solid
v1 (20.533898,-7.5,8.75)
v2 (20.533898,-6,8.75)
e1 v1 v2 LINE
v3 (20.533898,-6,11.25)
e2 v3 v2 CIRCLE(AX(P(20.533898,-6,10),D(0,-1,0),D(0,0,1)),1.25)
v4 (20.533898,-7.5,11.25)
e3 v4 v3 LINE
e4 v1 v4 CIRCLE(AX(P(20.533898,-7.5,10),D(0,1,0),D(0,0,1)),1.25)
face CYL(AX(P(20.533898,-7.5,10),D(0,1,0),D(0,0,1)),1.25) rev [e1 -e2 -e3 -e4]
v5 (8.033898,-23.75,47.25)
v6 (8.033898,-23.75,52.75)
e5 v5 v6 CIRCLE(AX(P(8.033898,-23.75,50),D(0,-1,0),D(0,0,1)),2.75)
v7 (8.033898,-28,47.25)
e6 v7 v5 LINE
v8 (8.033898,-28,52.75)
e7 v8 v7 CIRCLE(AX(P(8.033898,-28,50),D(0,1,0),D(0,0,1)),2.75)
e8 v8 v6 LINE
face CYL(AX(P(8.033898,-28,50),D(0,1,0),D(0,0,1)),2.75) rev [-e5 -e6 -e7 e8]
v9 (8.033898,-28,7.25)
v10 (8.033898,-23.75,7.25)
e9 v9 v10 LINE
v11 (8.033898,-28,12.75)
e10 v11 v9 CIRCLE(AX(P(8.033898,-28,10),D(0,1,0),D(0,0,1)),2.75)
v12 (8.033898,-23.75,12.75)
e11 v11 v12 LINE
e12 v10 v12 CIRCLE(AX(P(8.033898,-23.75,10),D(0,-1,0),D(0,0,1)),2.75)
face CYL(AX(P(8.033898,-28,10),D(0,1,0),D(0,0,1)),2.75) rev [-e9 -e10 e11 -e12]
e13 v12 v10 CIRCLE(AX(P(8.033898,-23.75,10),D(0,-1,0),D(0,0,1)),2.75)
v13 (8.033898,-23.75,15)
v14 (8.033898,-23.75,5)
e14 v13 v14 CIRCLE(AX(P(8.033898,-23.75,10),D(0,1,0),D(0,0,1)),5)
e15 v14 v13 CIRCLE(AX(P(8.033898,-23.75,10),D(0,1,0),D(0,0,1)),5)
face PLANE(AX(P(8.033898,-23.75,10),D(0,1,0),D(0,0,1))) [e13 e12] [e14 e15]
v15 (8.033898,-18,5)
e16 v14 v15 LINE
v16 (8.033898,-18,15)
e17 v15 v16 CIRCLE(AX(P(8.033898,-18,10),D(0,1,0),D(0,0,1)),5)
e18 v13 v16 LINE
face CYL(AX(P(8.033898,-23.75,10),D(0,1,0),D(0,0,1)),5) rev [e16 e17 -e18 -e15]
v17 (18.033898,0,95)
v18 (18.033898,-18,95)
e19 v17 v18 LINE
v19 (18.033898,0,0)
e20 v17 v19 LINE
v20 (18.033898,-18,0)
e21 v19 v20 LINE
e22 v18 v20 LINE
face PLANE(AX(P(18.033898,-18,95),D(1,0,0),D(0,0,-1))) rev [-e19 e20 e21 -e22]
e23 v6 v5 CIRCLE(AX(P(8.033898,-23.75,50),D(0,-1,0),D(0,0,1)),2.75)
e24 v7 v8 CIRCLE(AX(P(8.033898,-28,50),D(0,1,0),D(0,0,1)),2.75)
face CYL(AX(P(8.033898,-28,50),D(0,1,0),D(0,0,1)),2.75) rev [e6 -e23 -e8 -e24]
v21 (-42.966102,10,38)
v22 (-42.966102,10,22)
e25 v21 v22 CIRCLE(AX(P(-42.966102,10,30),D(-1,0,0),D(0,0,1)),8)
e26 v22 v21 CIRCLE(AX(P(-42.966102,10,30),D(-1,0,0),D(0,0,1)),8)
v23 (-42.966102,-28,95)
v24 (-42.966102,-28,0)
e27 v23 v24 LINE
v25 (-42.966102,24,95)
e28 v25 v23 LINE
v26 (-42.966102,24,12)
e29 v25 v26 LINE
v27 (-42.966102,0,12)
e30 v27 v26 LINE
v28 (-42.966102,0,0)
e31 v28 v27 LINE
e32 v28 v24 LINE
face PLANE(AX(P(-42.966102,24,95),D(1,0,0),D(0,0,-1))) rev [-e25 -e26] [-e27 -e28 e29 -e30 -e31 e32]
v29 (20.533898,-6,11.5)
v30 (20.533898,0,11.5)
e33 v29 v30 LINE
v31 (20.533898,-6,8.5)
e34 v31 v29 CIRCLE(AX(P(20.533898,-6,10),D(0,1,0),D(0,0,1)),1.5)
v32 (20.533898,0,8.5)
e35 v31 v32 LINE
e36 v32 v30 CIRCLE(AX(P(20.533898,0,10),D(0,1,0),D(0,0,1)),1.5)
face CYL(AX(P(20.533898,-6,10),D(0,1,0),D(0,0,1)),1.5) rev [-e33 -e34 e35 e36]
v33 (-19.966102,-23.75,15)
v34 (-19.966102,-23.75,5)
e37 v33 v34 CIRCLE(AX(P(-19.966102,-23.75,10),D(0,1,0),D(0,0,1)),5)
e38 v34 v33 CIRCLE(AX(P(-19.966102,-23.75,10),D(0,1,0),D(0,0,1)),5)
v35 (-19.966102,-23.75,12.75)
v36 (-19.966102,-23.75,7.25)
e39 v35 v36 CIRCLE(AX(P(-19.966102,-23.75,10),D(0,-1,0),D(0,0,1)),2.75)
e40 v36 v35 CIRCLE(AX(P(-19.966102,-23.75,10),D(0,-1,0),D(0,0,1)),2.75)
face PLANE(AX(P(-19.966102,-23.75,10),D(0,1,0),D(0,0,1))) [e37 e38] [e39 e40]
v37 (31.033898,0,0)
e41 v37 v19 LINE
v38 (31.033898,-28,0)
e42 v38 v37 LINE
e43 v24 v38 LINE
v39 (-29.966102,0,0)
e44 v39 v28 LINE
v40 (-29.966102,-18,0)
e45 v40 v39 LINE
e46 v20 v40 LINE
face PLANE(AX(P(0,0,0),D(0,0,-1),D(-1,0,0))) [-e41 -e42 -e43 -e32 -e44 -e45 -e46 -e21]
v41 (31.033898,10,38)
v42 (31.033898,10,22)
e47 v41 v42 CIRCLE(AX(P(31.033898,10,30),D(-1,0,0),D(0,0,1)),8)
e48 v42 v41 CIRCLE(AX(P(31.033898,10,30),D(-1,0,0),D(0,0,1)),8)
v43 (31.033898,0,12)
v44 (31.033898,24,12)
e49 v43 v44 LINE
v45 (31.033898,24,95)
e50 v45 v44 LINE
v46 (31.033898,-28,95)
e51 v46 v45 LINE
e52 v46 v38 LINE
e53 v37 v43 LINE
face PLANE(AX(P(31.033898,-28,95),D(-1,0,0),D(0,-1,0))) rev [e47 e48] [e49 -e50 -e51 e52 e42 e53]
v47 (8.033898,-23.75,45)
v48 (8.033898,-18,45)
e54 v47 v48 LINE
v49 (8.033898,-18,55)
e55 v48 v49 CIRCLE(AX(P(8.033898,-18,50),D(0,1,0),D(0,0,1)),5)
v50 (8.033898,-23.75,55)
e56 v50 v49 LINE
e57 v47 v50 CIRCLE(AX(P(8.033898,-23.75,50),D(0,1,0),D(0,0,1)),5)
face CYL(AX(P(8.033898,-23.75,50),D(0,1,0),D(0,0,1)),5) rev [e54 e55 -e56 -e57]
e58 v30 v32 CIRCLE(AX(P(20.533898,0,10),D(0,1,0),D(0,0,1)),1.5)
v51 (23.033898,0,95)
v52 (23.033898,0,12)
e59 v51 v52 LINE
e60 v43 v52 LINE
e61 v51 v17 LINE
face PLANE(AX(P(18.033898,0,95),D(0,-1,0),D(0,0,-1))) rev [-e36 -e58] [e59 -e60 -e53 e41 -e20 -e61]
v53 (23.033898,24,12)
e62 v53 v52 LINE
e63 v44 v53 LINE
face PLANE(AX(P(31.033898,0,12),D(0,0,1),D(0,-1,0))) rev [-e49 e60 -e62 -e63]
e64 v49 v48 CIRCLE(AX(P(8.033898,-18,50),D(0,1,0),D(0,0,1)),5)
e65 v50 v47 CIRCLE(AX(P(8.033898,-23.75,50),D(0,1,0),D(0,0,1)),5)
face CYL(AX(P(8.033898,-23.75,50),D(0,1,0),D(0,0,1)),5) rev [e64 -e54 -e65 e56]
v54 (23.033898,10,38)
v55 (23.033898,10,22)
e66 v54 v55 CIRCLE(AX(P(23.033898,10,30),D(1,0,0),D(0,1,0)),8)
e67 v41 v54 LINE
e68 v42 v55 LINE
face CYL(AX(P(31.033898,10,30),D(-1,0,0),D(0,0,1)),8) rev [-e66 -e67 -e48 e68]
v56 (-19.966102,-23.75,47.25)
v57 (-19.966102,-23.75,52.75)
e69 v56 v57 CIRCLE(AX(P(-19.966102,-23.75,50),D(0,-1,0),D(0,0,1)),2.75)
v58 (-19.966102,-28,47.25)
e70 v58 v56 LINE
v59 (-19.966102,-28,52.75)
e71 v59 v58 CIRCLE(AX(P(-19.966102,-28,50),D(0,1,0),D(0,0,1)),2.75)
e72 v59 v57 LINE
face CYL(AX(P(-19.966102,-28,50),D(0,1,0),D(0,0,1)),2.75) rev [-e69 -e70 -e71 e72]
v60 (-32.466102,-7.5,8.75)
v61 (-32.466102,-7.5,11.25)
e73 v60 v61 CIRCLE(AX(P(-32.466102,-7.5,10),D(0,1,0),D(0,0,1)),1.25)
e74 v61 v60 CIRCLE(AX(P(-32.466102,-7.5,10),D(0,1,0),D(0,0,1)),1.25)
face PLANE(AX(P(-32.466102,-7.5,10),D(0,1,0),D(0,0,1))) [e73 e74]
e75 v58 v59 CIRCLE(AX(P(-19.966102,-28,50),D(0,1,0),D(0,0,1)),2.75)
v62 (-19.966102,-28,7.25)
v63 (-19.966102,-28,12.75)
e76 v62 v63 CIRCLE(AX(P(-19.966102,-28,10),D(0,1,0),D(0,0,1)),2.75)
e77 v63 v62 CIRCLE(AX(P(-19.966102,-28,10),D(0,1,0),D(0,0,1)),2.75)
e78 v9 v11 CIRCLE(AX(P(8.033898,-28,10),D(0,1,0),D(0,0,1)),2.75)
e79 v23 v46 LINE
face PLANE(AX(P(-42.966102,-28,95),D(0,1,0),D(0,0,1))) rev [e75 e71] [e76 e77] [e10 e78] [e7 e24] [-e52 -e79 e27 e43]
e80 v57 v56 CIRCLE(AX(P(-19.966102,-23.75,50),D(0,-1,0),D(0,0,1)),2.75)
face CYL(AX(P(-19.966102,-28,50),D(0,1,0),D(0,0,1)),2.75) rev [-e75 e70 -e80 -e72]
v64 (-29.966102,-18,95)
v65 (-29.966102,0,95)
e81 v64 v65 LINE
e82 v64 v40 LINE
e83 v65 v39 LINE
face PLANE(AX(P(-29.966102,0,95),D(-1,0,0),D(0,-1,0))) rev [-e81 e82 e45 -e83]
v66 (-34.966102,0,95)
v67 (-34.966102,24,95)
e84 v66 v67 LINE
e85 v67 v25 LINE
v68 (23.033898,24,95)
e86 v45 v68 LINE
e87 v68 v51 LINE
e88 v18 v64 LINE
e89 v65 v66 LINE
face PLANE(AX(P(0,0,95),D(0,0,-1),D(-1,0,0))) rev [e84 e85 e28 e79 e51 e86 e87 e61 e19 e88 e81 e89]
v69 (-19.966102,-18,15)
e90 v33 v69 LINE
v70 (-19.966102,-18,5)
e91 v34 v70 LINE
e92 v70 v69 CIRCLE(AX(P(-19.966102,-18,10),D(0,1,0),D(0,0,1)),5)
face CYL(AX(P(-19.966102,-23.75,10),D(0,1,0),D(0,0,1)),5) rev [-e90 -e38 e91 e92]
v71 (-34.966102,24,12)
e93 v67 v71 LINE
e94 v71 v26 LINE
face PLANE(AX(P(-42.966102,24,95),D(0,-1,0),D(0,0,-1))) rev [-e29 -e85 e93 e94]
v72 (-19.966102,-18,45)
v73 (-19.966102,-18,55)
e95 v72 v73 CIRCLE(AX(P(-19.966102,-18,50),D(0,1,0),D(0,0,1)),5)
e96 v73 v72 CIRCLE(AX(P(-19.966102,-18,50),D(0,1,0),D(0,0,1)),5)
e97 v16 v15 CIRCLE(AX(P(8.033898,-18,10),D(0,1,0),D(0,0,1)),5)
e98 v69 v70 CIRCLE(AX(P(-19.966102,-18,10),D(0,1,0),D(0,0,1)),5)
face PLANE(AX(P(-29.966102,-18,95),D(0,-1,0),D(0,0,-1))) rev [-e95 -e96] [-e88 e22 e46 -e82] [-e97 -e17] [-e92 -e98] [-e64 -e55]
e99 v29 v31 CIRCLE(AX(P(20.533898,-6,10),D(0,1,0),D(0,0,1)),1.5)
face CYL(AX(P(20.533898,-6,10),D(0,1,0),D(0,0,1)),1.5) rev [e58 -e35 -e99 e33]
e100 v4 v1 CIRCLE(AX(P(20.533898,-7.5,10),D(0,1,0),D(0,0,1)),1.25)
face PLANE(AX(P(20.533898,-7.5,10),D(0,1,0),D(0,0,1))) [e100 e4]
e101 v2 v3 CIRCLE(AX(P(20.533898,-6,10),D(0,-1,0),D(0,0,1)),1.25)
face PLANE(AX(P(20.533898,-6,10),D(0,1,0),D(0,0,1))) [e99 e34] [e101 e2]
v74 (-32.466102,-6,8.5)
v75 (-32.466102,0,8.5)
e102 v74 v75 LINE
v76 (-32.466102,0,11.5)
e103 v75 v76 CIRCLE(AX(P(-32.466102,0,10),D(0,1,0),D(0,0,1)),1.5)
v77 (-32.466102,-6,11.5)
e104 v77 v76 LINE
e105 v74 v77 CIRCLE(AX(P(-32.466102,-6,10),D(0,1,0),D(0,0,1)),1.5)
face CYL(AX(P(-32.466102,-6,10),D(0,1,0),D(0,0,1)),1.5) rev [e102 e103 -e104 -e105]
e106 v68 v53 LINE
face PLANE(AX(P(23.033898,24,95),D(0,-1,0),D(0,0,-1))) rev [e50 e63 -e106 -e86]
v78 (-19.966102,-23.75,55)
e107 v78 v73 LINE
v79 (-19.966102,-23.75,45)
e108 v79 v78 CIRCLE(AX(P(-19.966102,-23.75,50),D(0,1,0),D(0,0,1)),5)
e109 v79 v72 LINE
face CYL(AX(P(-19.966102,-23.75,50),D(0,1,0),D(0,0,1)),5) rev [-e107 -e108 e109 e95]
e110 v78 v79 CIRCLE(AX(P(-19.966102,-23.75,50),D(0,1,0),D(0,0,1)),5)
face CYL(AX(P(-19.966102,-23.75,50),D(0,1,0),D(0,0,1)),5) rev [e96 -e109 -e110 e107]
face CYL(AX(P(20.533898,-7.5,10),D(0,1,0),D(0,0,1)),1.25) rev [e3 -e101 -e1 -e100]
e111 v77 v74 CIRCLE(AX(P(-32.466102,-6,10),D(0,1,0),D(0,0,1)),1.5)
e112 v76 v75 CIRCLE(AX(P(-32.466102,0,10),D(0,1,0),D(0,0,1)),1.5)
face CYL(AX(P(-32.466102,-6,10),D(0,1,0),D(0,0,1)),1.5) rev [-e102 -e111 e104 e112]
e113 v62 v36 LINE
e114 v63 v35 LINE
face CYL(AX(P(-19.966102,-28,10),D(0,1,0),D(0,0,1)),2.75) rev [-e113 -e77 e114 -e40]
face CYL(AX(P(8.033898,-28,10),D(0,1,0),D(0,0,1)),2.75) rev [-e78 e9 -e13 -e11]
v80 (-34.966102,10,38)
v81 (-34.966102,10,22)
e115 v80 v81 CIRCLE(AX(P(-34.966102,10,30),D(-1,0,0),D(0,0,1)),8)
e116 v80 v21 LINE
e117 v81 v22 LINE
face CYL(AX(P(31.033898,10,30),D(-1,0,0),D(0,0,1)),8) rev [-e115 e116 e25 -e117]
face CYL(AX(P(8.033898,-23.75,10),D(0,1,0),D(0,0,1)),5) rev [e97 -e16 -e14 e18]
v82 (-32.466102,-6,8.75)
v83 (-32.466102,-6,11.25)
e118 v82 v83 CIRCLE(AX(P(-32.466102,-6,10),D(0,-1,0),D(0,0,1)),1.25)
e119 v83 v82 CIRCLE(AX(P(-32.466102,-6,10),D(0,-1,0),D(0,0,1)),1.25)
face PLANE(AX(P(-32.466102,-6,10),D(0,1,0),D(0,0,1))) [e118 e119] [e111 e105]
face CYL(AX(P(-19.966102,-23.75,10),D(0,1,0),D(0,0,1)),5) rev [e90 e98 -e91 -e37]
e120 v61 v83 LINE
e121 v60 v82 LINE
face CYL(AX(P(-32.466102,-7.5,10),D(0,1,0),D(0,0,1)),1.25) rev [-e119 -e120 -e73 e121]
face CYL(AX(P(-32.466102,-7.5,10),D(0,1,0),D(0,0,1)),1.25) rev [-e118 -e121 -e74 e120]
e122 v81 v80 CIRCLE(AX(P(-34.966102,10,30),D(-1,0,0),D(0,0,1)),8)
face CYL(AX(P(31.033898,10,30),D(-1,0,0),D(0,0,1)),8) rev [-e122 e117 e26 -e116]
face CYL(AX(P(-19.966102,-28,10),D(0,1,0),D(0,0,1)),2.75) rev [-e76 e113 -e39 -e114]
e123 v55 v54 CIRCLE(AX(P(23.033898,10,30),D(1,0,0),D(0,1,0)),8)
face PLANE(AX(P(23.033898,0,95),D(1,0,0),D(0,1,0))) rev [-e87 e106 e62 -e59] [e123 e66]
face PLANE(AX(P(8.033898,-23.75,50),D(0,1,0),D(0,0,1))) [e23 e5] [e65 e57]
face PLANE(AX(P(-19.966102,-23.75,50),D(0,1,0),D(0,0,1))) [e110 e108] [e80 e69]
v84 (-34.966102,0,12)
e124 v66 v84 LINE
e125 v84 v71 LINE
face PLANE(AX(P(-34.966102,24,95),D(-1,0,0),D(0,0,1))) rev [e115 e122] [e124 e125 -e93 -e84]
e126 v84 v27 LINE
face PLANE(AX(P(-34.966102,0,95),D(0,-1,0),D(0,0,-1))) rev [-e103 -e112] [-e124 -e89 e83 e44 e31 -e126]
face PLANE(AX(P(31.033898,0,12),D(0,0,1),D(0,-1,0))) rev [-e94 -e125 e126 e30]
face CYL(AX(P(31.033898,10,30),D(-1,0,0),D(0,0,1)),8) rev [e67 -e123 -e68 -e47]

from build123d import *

# Parameters (mm, degrees)
EXTRUDE_1_DEPTH     = 95
SKETCH_2_R          = 2.75
CUT_EXTRUDE_1_DEPTH = 113.405897954
SKETCH_3_R          = 5
CUT_EXTRUDE_2_DEPTH = 5.75
SKETCH_4_W          = 12
SKETCH_4_H          = 24
CUT_EXTRUDE_3_DEPTH = 124.632519994
SKETCH_5_R          = 1.25
CUT_EXTRUDE_4_DEPTH = 7.5
SKETCH_6_R          = 1.5
CUT_EXTRUDE_5_DEPTH = 6
SKETCH_7_R          = 8
CUT_EXTRUDE_6_DEPTH = 124.632519994


with BuildPart() as part:
    # 草图1 → 凸台-拉伸1 (new body)
    with BuildSketch(Plane.XY):
        Polygon((-42.966101695, 24), (-42.966101695, -28), (31.033898305, -28), (31.033898305, 24), (23.033898305, 24), (23.033898305, 0), (18.033898305, 0), (18.033898305, -18), (-29.966101695, -18), (-29.966101695, 0), (-34.966101695, 0), (-34.966101695, 24), align=None)
    extrude(amount=EXTRUDE_1_DEPTH)

    # 草图2 → 切除-拉伸1 (cut, through all)
    with BuildSketch(Plane(origin=(0, -18, 0), x_dir=(1, 0, 0), z_dir=(0, 1, 0))):
        with Locations(Location((-19.966101695, -10, 0), (0, 0, 270))):
            Circle(SKETCH_2_R)
        with Locations(Location((-19.966101695, -50, 0), (0, 0, 270))):
            Circle(SKETCH_2_R)
        with Locations(Location((8.033898305, -10, 0), (0, 0, 270))):
            Circle(SKETCH_2_R)
        with Locations(Location((8.033898305, -50, 0), (0, 0, 270))):
            Circle(SKETCH_2_R)
    extrude(amount=-CUT_EXTRUDE_1_DEPTH, mode=Mode.SUBTRACT)

    # 草图3 → 切除-拉伸2 (cut)
    with BuildSketch(Plane(origin=(0, -18, 0), x_dir=(1, 0, 0), z_dir=(0, 1, 0))):
        with Locations(Location((-19.966101695, -10, 0), (0, 0, 270))):
            Circle(SKETCH_3_R)
        with Locations(Location((-19.966101695, -50, 0), (0, 0, 270))):
            Circle(SKETCH_3_R)
        with Locations(Location((8.033898305, -10, 0), (0, 0, 270))):
            Circle(SKETCH_3_R)
        with Locations(Location((8.033898305, -50, 0), (0, 0, 270))):
            Circle(SKETCH_3_R)
    extrude(amount=-CUT_EXTRUDE_2_DEPTH, mode=Mode.SUBTRACT)

    # 草图4 → 切除-拉伸3 (cut, through all)
    with BuildSketch(Plane.ZY.offset(42.966101695)):
        with Locations((6, 12)):
            Rectangle(SKETCH_4_W, SKETCH_4_H)
    extrude(amount=-CUT_EXTRUDE_3_DEPTH, mode=Mode.SUBTRACT)

    # 草图5 → 切除-拉伸4 (cut)
    with BuildSketch(Plane(origin=(0, 0, 0), x_dir=(1, 0, 0), z_dir=(0, 1, 0))):
        with Locations(Location((-32.466101695, -10, 0), (0, 0, 270))):
            Circle(SKETCH_5_R)
        with Locations(Location((20.533898305, -10, 0), (0, 0, 270))):
            Circle(SKETCH_5_R)
    extrude(amount=-CUT_EXTRUDE_4_DEPTH, mode=Mode.SUBTRACT)

    # 草图6 → 切除-拉伸5 (cut)
    with BuildSketch(Plane(origin=(0, 0, 0), x_dir=(1, 0, 0), z_dir=(0, 1, 0))):
        with Locations(Location((-32.466101695, -10, 0), (0, 0, 270))):
            Circle(SKETCH_6_R)
        with Locations(Location((20.533898305, -10, 0), (0, 0, 270))):
            Circle(SKETCH_6_R)
    extrude(amount=-CUT_EXTRUDE_5_DEPTH, mode=Mode.SUBTRACT)

    # 草图7 → 切除-拉伸6 (cut, through all)
    with BuildSketch(Plane.ZY.offset(42.966101695)):
        with Locations((30, 10)):
            Circle(SKETCH_7_R)
    extrude(amount=-CUT_EXTRUDE_6_DEPTH, mode=Mode.SUBTRACT)


solid = part.part
